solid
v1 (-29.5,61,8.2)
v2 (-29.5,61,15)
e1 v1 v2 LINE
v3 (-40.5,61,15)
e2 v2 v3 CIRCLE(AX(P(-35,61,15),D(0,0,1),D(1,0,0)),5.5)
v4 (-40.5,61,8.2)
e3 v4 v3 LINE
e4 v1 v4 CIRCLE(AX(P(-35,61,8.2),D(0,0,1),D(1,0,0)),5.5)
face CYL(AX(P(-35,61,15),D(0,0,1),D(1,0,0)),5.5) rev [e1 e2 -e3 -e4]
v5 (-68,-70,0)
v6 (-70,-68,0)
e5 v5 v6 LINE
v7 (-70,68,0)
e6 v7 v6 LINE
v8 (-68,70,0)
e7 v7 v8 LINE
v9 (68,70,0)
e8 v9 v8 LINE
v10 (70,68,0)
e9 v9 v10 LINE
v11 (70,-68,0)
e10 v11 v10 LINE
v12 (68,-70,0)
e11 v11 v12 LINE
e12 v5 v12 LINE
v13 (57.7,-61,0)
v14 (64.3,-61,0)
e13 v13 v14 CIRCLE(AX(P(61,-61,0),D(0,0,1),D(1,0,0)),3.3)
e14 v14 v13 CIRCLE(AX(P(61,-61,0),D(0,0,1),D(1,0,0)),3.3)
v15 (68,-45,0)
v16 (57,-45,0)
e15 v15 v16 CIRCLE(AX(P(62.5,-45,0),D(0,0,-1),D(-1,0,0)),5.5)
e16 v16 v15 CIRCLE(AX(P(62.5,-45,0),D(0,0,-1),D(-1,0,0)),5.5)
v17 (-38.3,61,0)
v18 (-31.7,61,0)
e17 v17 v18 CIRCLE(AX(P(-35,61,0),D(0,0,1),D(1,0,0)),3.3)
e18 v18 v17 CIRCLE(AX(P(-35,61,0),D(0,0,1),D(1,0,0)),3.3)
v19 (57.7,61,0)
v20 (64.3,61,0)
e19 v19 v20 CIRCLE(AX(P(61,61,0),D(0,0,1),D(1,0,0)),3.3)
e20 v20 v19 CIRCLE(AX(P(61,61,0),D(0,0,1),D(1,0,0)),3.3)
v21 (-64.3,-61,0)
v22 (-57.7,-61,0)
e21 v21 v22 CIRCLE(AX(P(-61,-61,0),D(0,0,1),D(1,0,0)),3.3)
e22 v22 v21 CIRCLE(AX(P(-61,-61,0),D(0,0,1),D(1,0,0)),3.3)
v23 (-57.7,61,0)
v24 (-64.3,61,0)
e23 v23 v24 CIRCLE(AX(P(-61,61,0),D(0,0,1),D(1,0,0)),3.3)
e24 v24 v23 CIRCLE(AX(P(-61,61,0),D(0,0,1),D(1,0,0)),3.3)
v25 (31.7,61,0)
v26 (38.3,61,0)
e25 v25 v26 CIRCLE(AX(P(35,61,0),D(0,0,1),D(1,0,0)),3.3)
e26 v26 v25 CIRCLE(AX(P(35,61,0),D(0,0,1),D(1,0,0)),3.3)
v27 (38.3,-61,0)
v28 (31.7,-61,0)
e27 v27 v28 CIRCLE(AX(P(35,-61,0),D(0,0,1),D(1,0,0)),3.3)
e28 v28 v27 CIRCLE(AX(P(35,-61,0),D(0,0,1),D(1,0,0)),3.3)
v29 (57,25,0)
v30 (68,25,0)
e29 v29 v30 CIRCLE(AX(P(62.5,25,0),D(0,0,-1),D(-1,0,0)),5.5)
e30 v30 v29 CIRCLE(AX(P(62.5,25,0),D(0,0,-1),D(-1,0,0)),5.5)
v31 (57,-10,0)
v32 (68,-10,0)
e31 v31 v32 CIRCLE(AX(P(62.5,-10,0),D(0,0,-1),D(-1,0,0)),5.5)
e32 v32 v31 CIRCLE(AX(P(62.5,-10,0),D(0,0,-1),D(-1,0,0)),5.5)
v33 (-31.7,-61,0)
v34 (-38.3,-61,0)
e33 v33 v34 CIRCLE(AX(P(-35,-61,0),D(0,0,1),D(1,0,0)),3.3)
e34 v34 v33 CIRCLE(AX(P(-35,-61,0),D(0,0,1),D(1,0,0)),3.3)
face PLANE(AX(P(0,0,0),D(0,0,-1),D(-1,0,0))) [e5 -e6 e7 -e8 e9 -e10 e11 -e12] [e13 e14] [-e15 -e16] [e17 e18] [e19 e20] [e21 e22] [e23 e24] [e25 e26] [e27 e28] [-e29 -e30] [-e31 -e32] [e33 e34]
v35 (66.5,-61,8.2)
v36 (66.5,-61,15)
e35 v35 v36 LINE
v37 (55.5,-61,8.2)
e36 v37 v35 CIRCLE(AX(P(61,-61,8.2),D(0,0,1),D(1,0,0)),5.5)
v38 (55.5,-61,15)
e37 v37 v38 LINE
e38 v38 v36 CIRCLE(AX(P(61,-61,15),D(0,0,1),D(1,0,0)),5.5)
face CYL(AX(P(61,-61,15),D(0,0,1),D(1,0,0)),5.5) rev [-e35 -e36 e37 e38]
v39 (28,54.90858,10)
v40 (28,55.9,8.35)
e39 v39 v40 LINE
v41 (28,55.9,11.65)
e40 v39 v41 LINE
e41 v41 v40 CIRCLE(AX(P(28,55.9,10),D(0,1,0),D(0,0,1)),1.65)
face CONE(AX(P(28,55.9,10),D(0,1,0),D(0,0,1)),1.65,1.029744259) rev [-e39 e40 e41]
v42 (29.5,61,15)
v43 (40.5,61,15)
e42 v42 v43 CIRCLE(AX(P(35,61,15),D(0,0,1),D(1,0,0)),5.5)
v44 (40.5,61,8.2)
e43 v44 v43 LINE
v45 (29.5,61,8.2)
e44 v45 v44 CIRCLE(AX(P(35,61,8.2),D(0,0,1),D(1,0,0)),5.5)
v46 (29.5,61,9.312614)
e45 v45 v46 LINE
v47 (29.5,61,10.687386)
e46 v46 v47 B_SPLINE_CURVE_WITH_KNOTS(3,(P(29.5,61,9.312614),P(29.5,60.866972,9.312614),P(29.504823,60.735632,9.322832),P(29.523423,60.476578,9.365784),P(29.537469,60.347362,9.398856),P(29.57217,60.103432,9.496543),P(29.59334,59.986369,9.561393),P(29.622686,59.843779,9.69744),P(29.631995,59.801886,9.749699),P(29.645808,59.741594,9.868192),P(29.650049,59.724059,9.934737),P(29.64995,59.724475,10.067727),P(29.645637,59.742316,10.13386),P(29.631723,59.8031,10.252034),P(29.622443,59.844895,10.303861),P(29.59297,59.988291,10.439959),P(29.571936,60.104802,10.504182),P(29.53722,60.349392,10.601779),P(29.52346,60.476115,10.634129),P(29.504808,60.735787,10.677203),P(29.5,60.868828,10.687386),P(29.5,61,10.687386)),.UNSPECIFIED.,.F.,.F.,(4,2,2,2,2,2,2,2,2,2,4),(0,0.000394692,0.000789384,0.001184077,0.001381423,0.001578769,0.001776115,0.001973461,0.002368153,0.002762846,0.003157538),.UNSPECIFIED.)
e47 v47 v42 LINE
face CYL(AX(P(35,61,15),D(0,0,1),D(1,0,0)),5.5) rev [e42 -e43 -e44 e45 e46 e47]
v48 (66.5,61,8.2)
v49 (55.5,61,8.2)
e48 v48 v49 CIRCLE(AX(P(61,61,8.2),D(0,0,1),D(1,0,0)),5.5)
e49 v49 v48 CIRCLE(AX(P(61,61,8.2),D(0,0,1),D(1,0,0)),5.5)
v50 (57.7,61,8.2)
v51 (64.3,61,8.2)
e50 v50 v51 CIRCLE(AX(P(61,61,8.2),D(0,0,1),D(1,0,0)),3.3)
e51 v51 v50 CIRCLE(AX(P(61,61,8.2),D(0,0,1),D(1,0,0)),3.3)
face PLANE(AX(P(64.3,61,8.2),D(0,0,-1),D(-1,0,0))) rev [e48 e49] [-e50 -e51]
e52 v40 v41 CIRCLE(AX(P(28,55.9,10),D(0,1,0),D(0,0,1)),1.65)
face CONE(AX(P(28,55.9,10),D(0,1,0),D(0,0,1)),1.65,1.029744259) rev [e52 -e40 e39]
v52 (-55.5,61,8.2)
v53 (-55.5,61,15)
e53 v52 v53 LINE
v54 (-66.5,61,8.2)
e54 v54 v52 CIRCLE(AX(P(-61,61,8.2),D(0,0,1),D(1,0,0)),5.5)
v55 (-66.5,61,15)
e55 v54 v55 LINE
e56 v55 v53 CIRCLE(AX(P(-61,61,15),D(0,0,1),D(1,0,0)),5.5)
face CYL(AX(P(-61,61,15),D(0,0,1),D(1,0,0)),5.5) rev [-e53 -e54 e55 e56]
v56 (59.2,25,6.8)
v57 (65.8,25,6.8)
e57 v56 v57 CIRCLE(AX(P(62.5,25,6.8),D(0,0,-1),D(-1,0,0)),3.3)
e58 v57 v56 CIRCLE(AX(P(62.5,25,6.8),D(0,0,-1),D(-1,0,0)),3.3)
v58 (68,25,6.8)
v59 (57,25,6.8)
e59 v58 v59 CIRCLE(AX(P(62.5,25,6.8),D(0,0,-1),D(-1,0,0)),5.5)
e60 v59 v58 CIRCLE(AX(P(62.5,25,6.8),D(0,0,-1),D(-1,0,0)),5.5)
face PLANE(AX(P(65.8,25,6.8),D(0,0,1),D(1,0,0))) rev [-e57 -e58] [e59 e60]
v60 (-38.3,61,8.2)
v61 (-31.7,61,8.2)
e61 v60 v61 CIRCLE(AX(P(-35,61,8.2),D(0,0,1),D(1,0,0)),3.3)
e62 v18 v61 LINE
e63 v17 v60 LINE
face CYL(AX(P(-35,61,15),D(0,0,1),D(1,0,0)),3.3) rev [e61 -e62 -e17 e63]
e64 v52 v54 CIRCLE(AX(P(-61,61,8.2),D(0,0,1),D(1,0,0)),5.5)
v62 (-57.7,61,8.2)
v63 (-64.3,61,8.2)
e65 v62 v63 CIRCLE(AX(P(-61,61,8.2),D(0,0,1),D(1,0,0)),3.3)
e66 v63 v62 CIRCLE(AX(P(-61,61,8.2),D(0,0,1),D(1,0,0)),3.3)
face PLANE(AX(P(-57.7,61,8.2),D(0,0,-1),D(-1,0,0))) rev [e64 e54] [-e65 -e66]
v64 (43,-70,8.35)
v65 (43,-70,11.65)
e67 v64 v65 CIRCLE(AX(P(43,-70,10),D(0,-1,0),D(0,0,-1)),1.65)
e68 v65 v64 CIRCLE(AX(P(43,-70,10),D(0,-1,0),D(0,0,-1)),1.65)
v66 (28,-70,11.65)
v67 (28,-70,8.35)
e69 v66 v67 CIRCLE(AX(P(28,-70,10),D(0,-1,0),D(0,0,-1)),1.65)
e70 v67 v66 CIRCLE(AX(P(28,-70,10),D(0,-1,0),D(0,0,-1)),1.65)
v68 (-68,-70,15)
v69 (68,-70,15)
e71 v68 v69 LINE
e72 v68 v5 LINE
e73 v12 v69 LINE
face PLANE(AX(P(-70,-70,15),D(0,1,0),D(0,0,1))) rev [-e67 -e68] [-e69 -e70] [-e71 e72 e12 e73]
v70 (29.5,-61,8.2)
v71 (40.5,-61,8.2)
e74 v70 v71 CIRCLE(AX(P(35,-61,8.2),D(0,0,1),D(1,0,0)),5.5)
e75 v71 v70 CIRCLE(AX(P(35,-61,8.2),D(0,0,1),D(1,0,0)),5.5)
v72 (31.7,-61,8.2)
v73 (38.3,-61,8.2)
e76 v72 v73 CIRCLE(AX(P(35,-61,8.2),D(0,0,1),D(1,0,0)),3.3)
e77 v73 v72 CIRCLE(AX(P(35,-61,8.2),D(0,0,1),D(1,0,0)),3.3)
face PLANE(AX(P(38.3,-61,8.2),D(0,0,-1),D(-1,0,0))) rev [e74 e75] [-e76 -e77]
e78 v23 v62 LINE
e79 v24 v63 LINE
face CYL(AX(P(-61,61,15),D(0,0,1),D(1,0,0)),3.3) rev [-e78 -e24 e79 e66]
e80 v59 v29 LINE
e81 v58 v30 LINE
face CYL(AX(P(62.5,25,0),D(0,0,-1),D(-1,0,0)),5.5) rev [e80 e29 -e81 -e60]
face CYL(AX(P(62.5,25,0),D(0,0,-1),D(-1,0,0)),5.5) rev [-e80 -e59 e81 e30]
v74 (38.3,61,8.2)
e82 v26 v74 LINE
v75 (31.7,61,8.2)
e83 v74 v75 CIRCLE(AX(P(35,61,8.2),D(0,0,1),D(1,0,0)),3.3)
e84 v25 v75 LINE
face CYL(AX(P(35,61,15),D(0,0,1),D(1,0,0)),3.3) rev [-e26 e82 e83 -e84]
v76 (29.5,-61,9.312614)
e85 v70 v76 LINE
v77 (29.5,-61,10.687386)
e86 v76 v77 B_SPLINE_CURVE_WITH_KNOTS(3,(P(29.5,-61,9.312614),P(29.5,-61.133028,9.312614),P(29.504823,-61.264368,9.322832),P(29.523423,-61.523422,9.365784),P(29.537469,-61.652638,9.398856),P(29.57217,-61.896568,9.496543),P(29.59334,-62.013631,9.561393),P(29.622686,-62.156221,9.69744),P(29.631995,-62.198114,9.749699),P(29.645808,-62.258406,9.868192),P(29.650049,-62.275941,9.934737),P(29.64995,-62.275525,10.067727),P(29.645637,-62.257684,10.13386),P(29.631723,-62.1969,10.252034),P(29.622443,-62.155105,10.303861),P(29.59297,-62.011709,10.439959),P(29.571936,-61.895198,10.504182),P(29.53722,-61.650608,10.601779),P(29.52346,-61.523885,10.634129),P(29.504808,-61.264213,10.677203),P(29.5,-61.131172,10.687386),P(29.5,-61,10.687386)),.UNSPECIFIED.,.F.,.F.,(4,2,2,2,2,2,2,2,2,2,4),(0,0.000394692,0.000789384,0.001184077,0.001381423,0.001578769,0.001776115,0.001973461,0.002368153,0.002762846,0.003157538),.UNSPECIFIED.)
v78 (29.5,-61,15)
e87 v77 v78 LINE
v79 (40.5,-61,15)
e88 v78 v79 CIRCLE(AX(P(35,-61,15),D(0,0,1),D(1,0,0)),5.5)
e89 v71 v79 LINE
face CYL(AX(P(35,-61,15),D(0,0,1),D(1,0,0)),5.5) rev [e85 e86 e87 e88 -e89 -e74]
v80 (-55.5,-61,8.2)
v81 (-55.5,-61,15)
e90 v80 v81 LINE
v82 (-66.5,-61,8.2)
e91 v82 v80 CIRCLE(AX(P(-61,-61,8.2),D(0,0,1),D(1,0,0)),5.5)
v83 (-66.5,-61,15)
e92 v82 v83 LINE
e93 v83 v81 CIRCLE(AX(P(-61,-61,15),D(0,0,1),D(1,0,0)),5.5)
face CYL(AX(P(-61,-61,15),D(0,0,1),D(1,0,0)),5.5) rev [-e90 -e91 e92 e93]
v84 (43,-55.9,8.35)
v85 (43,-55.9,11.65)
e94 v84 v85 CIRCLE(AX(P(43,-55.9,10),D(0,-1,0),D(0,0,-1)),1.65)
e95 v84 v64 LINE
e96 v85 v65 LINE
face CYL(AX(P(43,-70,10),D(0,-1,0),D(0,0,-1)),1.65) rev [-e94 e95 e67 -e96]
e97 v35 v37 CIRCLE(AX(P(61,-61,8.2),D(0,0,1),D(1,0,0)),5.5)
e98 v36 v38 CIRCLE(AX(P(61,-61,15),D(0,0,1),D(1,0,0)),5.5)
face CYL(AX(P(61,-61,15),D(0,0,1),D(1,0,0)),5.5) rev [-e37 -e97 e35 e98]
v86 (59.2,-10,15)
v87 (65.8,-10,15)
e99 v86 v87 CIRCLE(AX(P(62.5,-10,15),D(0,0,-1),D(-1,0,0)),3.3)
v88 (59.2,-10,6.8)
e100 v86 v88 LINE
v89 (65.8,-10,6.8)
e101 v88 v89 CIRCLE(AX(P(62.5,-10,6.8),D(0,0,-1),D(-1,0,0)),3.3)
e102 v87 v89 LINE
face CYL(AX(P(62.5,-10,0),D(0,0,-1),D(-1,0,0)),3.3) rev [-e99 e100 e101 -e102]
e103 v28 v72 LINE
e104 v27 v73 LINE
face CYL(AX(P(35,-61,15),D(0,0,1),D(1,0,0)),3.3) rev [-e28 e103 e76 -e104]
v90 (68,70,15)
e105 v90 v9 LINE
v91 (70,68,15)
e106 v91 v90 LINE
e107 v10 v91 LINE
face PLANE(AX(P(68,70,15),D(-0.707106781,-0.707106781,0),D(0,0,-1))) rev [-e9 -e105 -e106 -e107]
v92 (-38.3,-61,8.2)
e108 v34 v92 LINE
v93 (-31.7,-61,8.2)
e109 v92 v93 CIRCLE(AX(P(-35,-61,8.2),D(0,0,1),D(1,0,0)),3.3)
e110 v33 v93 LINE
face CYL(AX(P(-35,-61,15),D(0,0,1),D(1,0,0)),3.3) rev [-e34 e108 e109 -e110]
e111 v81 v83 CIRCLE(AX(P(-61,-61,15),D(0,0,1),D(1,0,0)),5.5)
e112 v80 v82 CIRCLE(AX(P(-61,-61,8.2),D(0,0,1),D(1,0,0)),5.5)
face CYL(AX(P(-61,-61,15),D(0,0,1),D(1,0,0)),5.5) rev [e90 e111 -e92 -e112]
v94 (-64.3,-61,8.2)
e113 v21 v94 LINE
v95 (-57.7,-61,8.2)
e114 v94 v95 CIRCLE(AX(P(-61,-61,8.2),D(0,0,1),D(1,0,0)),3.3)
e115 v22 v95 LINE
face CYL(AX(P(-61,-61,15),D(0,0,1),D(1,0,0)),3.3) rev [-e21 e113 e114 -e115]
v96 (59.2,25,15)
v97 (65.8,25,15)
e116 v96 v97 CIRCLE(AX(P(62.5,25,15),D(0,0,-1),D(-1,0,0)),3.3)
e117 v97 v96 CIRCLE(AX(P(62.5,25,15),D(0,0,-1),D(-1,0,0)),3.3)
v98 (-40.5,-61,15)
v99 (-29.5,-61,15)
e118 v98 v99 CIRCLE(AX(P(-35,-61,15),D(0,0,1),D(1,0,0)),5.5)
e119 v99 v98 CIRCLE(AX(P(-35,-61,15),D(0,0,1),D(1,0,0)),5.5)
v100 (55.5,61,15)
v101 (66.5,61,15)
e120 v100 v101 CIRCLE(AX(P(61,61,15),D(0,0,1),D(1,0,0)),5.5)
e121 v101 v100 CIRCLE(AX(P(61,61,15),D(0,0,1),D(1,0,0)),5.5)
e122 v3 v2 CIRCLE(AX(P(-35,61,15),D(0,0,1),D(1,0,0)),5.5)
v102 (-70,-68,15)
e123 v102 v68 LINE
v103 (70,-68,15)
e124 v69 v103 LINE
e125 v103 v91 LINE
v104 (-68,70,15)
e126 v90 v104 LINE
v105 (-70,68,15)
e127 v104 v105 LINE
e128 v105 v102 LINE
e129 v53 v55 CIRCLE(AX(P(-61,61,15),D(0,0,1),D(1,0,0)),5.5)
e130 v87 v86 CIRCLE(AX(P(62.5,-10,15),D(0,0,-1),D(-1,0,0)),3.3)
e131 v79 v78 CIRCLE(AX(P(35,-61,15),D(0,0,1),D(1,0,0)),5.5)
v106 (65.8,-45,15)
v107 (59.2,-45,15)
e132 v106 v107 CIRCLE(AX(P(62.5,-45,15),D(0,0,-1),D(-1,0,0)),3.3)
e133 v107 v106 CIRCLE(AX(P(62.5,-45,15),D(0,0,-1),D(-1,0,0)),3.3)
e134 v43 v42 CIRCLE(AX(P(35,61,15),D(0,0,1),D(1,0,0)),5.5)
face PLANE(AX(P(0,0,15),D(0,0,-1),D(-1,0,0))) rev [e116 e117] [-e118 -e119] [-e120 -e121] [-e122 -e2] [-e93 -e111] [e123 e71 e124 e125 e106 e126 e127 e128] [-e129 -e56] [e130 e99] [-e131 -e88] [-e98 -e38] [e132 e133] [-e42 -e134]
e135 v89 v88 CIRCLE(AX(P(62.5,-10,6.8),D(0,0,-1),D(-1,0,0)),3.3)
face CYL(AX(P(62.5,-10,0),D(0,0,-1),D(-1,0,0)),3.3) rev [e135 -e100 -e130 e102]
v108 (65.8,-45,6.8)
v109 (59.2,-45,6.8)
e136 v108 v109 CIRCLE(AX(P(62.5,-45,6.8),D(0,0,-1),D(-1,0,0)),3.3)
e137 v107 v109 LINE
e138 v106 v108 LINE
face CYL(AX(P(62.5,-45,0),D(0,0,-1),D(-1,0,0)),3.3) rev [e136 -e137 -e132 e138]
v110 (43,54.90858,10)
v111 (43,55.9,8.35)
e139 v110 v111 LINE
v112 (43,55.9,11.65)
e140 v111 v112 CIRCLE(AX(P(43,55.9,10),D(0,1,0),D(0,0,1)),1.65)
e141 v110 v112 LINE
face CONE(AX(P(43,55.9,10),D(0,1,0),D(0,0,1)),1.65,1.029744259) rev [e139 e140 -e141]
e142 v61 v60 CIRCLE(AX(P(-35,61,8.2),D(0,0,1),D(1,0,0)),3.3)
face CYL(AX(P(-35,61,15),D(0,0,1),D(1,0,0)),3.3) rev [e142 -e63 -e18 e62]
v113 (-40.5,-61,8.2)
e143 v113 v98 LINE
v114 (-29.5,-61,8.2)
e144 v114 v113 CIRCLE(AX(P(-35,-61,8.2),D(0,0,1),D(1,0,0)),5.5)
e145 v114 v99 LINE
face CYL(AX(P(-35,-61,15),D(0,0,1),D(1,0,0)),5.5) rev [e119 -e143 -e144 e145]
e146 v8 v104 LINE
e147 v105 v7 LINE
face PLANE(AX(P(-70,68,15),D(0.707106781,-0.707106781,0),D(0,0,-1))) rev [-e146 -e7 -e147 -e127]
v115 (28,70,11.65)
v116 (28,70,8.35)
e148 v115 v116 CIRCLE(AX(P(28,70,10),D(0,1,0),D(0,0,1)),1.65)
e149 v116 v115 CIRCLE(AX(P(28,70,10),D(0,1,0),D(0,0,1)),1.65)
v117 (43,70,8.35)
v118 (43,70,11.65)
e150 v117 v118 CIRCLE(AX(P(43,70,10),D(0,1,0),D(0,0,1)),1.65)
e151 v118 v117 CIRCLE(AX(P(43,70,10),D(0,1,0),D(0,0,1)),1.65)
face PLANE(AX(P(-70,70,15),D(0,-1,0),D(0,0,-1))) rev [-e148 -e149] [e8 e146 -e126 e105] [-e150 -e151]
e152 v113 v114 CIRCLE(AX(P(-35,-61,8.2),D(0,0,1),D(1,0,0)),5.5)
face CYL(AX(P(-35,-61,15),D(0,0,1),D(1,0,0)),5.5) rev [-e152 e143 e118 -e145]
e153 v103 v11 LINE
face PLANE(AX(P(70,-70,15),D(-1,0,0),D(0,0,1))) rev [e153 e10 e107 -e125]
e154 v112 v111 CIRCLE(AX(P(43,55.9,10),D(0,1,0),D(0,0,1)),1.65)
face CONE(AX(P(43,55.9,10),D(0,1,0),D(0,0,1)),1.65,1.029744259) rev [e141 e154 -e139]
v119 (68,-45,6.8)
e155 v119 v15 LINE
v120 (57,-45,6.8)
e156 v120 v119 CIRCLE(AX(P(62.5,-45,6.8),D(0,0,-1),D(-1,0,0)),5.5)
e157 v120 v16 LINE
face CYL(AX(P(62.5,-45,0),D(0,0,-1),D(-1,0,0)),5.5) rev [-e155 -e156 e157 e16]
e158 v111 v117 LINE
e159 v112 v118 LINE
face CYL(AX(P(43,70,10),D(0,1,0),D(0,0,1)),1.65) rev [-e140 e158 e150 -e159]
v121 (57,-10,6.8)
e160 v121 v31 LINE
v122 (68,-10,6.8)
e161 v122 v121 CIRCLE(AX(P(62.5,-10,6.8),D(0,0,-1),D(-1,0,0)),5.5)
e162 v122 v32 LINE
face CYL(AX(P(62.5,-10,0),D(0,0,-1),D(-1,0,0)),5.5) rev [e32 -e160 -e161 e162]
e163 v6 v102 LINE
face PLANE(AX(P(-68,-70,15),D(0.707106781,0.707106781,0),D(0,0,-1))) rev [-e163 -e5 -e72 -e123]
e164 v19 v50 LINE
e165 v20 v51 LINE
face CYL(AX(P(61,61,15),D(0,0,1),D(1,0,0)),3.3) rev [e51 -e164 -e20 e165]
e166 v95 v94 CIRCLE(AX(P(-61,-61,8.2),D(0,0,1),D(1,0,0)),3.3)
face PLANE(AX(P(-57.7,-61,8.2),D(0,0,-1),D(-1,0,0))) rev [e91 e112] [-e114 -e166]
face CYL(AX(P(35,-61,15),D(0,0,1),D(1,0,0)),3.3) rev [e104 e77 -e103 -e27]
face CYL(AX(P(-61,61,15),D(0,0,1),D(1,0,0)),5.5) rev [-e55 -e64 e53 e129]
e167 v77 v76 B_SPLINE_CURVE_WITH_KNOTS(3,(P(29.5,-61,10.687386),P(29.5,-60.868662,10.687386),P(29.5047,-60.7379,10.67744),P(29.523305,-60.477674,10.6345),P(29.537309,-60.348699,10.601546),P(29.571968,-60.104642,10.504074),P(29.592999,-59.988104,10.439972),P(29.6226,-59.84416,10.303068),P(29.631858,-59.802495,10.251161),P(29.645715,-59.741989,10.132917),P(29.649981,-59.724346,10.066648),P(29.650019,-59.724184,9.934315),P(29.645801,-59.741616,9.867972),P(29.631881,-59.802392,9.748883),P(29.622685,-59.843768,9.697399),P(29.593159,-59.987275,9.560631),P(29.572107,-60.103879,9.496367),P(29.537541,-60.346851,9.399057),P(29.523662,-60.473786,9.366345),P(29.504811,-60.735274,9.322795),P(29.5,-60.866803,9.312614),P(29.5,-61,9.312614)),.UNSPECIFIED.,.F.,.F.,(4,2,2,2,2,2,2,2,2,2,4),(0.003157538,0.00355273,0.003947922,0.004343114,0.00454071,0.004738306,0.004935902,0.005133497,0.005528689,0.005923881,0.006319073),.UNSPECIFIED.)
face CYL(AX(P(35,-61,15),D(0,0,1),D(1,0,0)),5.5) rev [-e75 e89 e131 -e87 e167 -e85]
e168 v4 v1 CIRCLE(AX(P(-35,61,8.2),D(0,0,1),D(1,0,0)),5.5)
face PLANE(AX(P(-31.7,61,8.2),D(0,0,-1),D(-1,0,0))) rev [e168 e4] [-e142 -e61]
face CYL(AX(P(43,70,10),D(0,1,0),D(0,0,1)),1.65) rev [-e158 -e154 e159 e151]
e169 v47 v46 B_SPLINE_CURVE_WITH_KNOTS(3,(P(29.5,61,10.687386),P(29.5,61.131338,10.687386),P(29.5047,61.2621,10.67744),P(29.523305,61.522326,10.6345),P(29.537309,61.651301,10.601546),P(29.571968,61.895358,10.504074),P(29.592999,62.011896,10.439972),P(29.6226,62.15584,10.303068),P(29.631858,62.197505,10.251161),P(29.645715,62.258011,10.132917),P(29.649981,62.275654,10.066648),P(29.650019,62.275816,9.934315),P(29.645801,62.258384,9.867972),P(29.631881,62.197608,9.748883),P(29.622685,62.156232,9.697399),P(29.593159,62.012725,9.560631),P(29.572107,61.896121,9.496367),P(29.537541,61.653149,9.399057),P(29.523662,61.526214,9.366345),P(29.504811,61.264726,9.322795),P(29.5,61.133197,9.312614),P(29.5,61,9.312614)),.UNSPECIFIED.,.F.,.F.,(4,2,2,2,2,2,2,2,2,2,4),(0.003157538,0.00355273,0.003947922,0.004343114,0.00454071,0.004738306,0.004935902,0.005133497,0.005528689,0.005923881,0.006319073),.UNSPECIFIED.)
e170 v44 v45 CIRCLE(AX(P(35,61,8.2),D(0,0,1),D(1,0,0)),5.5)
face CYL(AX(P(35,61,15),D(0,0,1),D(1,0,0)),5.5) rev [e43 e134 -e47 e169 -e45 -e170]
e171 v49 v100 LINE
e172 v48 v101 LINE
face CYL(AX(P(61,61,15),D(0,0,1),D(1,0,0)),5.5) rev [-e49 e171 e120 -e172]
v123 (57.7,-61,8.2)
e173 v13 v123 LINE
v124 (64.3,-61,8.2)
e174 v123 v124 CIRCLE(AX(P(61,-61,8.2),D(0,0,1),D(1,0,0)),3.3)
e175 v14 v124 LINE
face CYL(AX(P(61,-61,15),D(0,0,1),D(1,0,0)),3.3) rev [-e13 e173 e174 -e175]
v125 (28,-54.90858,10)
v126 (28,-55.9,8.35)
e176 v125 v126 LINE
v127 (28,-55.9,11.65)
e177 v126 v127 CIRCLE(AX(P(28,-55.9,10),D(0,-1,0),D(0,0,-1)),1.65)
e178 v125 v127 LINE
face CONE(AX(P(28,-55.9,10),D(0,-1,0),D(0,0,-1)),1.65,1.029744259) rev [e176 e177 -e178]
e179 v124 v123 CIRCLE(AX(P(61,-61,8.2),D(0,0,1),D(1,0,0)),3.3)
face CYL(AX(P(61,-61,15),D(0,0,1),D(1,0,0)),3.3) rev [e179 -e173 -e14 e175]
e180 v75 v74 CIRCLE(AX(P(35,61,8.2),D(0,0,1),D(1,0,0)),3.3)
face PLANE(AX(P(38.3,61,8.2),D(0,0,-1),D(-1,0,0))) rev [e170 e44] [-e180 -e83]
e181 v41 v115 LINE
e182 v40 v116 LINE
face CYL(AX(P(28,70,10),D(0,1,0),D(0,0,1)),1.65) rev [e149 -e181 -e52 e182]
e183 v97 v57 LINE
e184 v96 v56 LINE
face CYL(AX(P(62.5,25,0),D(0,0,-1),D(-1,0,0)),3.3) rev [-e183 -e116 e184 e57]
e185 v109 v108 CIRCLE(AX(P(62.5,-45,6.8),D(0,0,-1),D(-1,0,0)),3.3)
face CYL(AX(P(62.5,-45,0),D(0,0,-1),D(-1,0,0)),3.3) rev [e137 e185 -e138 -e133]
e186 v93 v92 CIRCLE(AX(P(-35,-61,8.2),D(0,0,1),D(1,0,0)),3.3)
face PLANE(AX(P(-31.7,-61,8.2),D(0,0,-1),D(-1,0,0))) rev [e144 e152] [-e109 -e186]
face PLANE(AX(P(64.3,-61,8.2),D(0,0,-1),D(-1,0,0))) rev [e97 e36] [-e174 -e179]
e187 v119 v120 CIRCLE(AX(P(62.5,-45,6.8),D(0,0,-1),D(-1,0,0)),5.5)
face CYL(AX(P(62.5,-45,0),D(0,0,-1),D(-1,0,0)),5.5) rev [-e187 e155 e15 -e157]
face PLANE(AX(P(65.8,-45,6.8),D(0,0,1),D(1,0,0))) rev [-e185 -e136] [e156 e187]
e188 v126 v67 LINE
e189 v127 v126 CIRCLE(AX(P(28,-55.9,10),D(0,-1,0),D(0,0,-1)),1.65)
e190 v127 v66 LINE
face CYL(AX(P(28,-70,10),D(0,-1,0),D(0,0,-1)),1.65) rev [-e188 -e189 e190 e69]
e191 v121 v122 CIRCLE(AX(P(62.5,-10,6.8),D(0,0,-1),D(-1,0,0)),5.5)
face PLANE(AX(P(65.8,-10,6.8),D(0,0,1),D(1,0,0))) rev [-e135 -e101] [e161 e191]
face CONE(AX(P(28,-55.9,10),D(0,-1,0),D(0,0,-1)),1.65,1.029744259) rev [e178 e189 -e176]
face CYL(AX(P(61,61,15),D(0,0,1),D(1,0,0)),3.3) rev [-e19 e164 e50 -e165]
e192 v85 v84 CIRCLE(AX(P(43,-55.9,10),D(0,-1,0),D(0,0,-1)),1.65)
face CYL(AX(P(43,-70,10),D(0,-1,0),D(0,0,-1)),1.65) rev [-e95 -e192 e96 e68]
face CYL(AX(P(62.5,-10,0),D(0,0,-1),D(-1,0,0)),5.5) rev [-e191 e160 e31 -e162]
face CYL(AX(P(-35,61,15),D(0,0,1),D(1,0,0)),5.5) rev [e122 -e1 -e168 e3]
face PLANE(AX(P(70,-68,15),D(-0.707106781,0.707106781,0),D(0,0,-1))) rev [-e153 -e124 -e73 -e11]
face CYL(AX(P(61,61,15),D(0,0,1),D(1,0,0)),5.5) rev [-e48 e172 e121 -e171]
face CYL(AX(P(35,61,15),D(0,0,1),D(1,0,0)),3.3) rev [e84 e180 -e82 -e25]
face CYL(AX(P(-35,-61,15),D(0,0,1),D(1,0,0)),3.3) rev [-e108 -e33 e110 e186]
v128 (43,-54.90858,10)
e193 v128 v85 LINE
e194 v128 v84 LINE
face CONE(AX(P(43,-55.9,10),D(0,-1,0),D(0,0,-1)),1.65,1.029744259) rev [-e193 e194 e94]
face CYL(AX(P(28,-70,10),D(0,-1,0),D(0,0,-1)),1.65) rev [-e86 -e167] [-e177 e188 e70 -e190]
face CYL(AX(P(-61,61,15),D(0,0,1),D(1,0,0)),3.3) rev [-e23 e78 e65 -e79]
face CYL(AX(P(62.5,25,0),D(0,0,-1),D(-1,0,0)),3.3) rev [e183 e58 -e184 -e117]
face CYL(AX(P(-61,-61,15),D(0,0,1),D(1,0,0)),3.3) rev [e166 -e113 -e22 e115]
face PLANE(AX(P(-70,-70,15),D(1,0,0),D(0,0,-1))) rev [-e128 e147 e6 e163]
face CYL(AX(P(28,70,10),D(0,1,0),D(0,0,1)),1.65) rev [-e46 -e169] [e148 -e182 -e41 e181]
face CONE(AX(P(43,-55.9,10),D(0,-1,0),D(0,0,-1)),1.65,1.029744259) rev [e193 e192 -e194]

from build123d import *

# Parameters (mm, degrees)
SKETCH_1_W                  = 140
SKETCH_1_H                  = 140
EXTRUDE_1_DEPTH             = 15
HOLE_WIZARD_1_AT_2_COUNT    = 2
HOLE_WIZARD_1_AT_2_PITCH    = 26
HOLE_WIZARD_1_AT_3_COUNT    = 2
HOLE_WIZARD_1_AT_3_PITCH    = 96
HOLE_WIZARD_1_AT_4_COUNT    = 2
HOLE_WIZARD_1_AT_4_PITCH    = 122
PATTERN_LINEAR_1_COUNT      = 2
PATTERN_LINEAR_1_PITCH      = 122
HOLE_WIZARD_2_D             = 6.6
HOLE_WIZARD_2_CBORE_D       = 11
HOLE_WIZARD_2_CBORE_DEPTH   = 6.8
HOLE_WIZARD_M4_1_AT_2_COUNT = 2
HOLE_WIZARD_M4_1_AT_2_PITCH = 15
CHAMFER_1_SIZE              = 2


with BuildPart() as part:
    # 草图1 → 凸台-拉伸1 (new body)
    with BuildSketch(Plane.XY):
        Rectangle(SKETCH_1_W, SKETCH_1_H)
    extrude(amount=EXTRUDE_1_DEPTH)

    # 草图2 → 打孔尺寸(%根据)内六角圆柱头螺钉的类型1 (revolve, cut)
    with BuildSketch(Plane(origin=(-61, 61, 15), x_dir=(0, -1, 0), z_dir=(1, 0, 0))):
        Polygon((0, 0), (0, 16.982840043), (3.3, 15), (3.3, 6.8), (5.5, 6.8), (5.5, 0), align=None)
    hole_wizard_1 = revolve(axis=Axis((-61, 61, 21.35), (0, 0, -1)), mode=Mode.SUBTRACT)

    # 打孔尺寸(%根据)内六角圆柱头螺钉的类型1 at 2: 打孔尺寸(%根据)内六角圆柱头螺钉的类型1 ×2
    with Locations(*[(i * HOLE_WIZARD_1_AT_2_PITCH, 0, 0) for i in range(1, HOLE_WIZARD_1_AT_2_COUNT)]):
        add(hole_wizard_1, mode=Mode.SUBTRACT)

    # 打孔尺寸(%根据)内六角圆柱头螺钉的类型1 at 3: 打孔尺寸(%根据)内六角圆柱头螺钉的类型1 ×2
    with Locations(*[(i * HOLE_WIZARD_1_AT_3_PITCH, 0, 0) for i in range(1, HOLE_WIZARD_1_AT_3_COUNT)]):
        add(hole_wizard_1, mode=Mode.SUBTRACT)

    # 打孔尺寸(%根据)内六角圆柱头螺钉的类型1 at 4: 打孔尺寸(%根据)内六角圆柱头螺钉的类型1 ×2
    with Locations(*[(i * HOLE_WIZARD_1_AT_4_PITCH, 0, 0) for i in range(1, HOLE_WIZARD_1_AT_4_COUNT)]):
        add(hole_wizard_1, mode=Mode.SUBTRACT)

    # 阵列(线性)1: 打孔尺寸(%根据)内六角圆柱头螺钉的类型1 ×2
    with Locations(*[(0, -i * PATTERN_LINEAR_1_PITCH, 0) for i in range(1, PATTERN_LINEAR_1_COUNT)]):
        add(hole_wizard_1, mode=Mode.SUBTRACT)

    # 阵列(线性)1 copy 1 sketch → 阵列(线性)1 copy 1 (revolve, cut)
    with BuildSketch(Plane(origin=(-35, -61, 15), x_dir=(0, -1, 0), z_dir=(1, 0, 0))):
        Polygon((0, 0), (0, 16.982840043), (3.3, 15), (3.3, 6.8), (5.5, 6.8), (5.5, 0), align=None)
    revolve(axis=Axis((-35, -61, 21.35), (0, 0, -1)), mode=Mode.SUBTRACT)

    # 阵列(线性)1 copy 2 sketch → 阵列(线性)1 copy 2 (revolve, cut)
    with BuildSketch(Plane(origin=(35, -61, 15), x_dir=(0, -1, 0), z_dir=(1, 0, 0))):
        Polygon((0, 0), (0, 16.982840043), (3.3, 15), (3.3, 6.8), (5.5, 6.8), (5.5, 0), align=None)
    revolve(axis=Axis((35, -61, 21.35), (0, 0, -1)), mode=Mode.SUBTRACT)

    # 阵列(线性)1 copy 3 sketch → 阵列(线性)1 copy 3 (revolve, cut)
    with BuildSketch(Plane(origin=(61, -61, 15), x_dir=(0, -1, 0), z_dir=(1, 0, 0))):
        Polygon((0, 0), (0, 16.982840043), (3.3, 15), (3.3, 6.8), (5.5, 6.8), (5.5, 0), align=None)
    revolve(axis=Axis((61, -61, 21.35), (0, 0, -1)), mode=Mode.SUBTRACT)

    # 打孔尺寸(%根据)内六角圆柱头螺钉的类型2 (through all)
    with Locations(Plane(origin=(0, 0, 0), x_dir=(-1, 0, 0), z_dir=(0, 0, -1))):
        with Locations((-62.5, 25), (-62.5, -10), (-62.5, -45)):
            CounterBoreHole(HOLE_WIZARD_2_D / 2, HOLE_WIZARD_2_CBORE_D / 2, HOLE_WIZARD_2_CBORE_DEPTH)

    # 草图7 → M4 螺纹孔1 (revolve, cut)
    with BuildSketch(Plane(origin=(28, 70, 10), x_dir=(0, 0, 1), z_dir=(1, 0, 0))):
        Polygon((0, 0), (0, 15.091420021), (1.65, 14.1), (1.65, 0), align=None)
    hole_wizard_m4_1 = revolve(axis=Axis((28, 76.35, 10), (0, -1, 0)), mode=Mode.SUBTRACT)

    # M4 螺纹孔1 at 2: M4 螺纹孔1 ×2
    with Locations(*[(i * HOLE_WIZARD_M4_1_AT_2_PITCH, 0, 0) for i in range(1, HOLE_WIZARD_M4_1_AT_2_COUNT)]):
        add(hole_wizard_m4_1, mode=Mode.SUBTRACT)

    # 倒角1
    chamfer_1_edges = [part.edges().sort_by_distance(p)[0] for p in [
        (70, -70, 7.5),
        (-70, -70, 7.5),
        (-70, 70, 7.5),
        (70, 70, 7.5),
    ]]
    chamfer(chamfer_1_edges, length=CHAMFER_1_SIZE)

    # 镜向1: M4 螺纹孔1 across plane
    add(hole_wizard_m4_1.mirror(Plane.ZX), mode=Mode.SUBTRACT)

    # 镜向1 copy 1 sketch → 镜向1 copy 1 (revolve, cut)
    with BuildSketch(Plane(origin=(43, -70, 10), x_dir=(0, 0, 1), z_dir=(1, 0, 0))):
        Polygon((0, 0), (0, -15.091420021), (1.65, -14.1), (1.65, 0), align=None)
    revolve(axis=Axis((43, -76.35, 10), (0, -1, 0)), mode=Mode.SUBTRACT)


solid = part.part
